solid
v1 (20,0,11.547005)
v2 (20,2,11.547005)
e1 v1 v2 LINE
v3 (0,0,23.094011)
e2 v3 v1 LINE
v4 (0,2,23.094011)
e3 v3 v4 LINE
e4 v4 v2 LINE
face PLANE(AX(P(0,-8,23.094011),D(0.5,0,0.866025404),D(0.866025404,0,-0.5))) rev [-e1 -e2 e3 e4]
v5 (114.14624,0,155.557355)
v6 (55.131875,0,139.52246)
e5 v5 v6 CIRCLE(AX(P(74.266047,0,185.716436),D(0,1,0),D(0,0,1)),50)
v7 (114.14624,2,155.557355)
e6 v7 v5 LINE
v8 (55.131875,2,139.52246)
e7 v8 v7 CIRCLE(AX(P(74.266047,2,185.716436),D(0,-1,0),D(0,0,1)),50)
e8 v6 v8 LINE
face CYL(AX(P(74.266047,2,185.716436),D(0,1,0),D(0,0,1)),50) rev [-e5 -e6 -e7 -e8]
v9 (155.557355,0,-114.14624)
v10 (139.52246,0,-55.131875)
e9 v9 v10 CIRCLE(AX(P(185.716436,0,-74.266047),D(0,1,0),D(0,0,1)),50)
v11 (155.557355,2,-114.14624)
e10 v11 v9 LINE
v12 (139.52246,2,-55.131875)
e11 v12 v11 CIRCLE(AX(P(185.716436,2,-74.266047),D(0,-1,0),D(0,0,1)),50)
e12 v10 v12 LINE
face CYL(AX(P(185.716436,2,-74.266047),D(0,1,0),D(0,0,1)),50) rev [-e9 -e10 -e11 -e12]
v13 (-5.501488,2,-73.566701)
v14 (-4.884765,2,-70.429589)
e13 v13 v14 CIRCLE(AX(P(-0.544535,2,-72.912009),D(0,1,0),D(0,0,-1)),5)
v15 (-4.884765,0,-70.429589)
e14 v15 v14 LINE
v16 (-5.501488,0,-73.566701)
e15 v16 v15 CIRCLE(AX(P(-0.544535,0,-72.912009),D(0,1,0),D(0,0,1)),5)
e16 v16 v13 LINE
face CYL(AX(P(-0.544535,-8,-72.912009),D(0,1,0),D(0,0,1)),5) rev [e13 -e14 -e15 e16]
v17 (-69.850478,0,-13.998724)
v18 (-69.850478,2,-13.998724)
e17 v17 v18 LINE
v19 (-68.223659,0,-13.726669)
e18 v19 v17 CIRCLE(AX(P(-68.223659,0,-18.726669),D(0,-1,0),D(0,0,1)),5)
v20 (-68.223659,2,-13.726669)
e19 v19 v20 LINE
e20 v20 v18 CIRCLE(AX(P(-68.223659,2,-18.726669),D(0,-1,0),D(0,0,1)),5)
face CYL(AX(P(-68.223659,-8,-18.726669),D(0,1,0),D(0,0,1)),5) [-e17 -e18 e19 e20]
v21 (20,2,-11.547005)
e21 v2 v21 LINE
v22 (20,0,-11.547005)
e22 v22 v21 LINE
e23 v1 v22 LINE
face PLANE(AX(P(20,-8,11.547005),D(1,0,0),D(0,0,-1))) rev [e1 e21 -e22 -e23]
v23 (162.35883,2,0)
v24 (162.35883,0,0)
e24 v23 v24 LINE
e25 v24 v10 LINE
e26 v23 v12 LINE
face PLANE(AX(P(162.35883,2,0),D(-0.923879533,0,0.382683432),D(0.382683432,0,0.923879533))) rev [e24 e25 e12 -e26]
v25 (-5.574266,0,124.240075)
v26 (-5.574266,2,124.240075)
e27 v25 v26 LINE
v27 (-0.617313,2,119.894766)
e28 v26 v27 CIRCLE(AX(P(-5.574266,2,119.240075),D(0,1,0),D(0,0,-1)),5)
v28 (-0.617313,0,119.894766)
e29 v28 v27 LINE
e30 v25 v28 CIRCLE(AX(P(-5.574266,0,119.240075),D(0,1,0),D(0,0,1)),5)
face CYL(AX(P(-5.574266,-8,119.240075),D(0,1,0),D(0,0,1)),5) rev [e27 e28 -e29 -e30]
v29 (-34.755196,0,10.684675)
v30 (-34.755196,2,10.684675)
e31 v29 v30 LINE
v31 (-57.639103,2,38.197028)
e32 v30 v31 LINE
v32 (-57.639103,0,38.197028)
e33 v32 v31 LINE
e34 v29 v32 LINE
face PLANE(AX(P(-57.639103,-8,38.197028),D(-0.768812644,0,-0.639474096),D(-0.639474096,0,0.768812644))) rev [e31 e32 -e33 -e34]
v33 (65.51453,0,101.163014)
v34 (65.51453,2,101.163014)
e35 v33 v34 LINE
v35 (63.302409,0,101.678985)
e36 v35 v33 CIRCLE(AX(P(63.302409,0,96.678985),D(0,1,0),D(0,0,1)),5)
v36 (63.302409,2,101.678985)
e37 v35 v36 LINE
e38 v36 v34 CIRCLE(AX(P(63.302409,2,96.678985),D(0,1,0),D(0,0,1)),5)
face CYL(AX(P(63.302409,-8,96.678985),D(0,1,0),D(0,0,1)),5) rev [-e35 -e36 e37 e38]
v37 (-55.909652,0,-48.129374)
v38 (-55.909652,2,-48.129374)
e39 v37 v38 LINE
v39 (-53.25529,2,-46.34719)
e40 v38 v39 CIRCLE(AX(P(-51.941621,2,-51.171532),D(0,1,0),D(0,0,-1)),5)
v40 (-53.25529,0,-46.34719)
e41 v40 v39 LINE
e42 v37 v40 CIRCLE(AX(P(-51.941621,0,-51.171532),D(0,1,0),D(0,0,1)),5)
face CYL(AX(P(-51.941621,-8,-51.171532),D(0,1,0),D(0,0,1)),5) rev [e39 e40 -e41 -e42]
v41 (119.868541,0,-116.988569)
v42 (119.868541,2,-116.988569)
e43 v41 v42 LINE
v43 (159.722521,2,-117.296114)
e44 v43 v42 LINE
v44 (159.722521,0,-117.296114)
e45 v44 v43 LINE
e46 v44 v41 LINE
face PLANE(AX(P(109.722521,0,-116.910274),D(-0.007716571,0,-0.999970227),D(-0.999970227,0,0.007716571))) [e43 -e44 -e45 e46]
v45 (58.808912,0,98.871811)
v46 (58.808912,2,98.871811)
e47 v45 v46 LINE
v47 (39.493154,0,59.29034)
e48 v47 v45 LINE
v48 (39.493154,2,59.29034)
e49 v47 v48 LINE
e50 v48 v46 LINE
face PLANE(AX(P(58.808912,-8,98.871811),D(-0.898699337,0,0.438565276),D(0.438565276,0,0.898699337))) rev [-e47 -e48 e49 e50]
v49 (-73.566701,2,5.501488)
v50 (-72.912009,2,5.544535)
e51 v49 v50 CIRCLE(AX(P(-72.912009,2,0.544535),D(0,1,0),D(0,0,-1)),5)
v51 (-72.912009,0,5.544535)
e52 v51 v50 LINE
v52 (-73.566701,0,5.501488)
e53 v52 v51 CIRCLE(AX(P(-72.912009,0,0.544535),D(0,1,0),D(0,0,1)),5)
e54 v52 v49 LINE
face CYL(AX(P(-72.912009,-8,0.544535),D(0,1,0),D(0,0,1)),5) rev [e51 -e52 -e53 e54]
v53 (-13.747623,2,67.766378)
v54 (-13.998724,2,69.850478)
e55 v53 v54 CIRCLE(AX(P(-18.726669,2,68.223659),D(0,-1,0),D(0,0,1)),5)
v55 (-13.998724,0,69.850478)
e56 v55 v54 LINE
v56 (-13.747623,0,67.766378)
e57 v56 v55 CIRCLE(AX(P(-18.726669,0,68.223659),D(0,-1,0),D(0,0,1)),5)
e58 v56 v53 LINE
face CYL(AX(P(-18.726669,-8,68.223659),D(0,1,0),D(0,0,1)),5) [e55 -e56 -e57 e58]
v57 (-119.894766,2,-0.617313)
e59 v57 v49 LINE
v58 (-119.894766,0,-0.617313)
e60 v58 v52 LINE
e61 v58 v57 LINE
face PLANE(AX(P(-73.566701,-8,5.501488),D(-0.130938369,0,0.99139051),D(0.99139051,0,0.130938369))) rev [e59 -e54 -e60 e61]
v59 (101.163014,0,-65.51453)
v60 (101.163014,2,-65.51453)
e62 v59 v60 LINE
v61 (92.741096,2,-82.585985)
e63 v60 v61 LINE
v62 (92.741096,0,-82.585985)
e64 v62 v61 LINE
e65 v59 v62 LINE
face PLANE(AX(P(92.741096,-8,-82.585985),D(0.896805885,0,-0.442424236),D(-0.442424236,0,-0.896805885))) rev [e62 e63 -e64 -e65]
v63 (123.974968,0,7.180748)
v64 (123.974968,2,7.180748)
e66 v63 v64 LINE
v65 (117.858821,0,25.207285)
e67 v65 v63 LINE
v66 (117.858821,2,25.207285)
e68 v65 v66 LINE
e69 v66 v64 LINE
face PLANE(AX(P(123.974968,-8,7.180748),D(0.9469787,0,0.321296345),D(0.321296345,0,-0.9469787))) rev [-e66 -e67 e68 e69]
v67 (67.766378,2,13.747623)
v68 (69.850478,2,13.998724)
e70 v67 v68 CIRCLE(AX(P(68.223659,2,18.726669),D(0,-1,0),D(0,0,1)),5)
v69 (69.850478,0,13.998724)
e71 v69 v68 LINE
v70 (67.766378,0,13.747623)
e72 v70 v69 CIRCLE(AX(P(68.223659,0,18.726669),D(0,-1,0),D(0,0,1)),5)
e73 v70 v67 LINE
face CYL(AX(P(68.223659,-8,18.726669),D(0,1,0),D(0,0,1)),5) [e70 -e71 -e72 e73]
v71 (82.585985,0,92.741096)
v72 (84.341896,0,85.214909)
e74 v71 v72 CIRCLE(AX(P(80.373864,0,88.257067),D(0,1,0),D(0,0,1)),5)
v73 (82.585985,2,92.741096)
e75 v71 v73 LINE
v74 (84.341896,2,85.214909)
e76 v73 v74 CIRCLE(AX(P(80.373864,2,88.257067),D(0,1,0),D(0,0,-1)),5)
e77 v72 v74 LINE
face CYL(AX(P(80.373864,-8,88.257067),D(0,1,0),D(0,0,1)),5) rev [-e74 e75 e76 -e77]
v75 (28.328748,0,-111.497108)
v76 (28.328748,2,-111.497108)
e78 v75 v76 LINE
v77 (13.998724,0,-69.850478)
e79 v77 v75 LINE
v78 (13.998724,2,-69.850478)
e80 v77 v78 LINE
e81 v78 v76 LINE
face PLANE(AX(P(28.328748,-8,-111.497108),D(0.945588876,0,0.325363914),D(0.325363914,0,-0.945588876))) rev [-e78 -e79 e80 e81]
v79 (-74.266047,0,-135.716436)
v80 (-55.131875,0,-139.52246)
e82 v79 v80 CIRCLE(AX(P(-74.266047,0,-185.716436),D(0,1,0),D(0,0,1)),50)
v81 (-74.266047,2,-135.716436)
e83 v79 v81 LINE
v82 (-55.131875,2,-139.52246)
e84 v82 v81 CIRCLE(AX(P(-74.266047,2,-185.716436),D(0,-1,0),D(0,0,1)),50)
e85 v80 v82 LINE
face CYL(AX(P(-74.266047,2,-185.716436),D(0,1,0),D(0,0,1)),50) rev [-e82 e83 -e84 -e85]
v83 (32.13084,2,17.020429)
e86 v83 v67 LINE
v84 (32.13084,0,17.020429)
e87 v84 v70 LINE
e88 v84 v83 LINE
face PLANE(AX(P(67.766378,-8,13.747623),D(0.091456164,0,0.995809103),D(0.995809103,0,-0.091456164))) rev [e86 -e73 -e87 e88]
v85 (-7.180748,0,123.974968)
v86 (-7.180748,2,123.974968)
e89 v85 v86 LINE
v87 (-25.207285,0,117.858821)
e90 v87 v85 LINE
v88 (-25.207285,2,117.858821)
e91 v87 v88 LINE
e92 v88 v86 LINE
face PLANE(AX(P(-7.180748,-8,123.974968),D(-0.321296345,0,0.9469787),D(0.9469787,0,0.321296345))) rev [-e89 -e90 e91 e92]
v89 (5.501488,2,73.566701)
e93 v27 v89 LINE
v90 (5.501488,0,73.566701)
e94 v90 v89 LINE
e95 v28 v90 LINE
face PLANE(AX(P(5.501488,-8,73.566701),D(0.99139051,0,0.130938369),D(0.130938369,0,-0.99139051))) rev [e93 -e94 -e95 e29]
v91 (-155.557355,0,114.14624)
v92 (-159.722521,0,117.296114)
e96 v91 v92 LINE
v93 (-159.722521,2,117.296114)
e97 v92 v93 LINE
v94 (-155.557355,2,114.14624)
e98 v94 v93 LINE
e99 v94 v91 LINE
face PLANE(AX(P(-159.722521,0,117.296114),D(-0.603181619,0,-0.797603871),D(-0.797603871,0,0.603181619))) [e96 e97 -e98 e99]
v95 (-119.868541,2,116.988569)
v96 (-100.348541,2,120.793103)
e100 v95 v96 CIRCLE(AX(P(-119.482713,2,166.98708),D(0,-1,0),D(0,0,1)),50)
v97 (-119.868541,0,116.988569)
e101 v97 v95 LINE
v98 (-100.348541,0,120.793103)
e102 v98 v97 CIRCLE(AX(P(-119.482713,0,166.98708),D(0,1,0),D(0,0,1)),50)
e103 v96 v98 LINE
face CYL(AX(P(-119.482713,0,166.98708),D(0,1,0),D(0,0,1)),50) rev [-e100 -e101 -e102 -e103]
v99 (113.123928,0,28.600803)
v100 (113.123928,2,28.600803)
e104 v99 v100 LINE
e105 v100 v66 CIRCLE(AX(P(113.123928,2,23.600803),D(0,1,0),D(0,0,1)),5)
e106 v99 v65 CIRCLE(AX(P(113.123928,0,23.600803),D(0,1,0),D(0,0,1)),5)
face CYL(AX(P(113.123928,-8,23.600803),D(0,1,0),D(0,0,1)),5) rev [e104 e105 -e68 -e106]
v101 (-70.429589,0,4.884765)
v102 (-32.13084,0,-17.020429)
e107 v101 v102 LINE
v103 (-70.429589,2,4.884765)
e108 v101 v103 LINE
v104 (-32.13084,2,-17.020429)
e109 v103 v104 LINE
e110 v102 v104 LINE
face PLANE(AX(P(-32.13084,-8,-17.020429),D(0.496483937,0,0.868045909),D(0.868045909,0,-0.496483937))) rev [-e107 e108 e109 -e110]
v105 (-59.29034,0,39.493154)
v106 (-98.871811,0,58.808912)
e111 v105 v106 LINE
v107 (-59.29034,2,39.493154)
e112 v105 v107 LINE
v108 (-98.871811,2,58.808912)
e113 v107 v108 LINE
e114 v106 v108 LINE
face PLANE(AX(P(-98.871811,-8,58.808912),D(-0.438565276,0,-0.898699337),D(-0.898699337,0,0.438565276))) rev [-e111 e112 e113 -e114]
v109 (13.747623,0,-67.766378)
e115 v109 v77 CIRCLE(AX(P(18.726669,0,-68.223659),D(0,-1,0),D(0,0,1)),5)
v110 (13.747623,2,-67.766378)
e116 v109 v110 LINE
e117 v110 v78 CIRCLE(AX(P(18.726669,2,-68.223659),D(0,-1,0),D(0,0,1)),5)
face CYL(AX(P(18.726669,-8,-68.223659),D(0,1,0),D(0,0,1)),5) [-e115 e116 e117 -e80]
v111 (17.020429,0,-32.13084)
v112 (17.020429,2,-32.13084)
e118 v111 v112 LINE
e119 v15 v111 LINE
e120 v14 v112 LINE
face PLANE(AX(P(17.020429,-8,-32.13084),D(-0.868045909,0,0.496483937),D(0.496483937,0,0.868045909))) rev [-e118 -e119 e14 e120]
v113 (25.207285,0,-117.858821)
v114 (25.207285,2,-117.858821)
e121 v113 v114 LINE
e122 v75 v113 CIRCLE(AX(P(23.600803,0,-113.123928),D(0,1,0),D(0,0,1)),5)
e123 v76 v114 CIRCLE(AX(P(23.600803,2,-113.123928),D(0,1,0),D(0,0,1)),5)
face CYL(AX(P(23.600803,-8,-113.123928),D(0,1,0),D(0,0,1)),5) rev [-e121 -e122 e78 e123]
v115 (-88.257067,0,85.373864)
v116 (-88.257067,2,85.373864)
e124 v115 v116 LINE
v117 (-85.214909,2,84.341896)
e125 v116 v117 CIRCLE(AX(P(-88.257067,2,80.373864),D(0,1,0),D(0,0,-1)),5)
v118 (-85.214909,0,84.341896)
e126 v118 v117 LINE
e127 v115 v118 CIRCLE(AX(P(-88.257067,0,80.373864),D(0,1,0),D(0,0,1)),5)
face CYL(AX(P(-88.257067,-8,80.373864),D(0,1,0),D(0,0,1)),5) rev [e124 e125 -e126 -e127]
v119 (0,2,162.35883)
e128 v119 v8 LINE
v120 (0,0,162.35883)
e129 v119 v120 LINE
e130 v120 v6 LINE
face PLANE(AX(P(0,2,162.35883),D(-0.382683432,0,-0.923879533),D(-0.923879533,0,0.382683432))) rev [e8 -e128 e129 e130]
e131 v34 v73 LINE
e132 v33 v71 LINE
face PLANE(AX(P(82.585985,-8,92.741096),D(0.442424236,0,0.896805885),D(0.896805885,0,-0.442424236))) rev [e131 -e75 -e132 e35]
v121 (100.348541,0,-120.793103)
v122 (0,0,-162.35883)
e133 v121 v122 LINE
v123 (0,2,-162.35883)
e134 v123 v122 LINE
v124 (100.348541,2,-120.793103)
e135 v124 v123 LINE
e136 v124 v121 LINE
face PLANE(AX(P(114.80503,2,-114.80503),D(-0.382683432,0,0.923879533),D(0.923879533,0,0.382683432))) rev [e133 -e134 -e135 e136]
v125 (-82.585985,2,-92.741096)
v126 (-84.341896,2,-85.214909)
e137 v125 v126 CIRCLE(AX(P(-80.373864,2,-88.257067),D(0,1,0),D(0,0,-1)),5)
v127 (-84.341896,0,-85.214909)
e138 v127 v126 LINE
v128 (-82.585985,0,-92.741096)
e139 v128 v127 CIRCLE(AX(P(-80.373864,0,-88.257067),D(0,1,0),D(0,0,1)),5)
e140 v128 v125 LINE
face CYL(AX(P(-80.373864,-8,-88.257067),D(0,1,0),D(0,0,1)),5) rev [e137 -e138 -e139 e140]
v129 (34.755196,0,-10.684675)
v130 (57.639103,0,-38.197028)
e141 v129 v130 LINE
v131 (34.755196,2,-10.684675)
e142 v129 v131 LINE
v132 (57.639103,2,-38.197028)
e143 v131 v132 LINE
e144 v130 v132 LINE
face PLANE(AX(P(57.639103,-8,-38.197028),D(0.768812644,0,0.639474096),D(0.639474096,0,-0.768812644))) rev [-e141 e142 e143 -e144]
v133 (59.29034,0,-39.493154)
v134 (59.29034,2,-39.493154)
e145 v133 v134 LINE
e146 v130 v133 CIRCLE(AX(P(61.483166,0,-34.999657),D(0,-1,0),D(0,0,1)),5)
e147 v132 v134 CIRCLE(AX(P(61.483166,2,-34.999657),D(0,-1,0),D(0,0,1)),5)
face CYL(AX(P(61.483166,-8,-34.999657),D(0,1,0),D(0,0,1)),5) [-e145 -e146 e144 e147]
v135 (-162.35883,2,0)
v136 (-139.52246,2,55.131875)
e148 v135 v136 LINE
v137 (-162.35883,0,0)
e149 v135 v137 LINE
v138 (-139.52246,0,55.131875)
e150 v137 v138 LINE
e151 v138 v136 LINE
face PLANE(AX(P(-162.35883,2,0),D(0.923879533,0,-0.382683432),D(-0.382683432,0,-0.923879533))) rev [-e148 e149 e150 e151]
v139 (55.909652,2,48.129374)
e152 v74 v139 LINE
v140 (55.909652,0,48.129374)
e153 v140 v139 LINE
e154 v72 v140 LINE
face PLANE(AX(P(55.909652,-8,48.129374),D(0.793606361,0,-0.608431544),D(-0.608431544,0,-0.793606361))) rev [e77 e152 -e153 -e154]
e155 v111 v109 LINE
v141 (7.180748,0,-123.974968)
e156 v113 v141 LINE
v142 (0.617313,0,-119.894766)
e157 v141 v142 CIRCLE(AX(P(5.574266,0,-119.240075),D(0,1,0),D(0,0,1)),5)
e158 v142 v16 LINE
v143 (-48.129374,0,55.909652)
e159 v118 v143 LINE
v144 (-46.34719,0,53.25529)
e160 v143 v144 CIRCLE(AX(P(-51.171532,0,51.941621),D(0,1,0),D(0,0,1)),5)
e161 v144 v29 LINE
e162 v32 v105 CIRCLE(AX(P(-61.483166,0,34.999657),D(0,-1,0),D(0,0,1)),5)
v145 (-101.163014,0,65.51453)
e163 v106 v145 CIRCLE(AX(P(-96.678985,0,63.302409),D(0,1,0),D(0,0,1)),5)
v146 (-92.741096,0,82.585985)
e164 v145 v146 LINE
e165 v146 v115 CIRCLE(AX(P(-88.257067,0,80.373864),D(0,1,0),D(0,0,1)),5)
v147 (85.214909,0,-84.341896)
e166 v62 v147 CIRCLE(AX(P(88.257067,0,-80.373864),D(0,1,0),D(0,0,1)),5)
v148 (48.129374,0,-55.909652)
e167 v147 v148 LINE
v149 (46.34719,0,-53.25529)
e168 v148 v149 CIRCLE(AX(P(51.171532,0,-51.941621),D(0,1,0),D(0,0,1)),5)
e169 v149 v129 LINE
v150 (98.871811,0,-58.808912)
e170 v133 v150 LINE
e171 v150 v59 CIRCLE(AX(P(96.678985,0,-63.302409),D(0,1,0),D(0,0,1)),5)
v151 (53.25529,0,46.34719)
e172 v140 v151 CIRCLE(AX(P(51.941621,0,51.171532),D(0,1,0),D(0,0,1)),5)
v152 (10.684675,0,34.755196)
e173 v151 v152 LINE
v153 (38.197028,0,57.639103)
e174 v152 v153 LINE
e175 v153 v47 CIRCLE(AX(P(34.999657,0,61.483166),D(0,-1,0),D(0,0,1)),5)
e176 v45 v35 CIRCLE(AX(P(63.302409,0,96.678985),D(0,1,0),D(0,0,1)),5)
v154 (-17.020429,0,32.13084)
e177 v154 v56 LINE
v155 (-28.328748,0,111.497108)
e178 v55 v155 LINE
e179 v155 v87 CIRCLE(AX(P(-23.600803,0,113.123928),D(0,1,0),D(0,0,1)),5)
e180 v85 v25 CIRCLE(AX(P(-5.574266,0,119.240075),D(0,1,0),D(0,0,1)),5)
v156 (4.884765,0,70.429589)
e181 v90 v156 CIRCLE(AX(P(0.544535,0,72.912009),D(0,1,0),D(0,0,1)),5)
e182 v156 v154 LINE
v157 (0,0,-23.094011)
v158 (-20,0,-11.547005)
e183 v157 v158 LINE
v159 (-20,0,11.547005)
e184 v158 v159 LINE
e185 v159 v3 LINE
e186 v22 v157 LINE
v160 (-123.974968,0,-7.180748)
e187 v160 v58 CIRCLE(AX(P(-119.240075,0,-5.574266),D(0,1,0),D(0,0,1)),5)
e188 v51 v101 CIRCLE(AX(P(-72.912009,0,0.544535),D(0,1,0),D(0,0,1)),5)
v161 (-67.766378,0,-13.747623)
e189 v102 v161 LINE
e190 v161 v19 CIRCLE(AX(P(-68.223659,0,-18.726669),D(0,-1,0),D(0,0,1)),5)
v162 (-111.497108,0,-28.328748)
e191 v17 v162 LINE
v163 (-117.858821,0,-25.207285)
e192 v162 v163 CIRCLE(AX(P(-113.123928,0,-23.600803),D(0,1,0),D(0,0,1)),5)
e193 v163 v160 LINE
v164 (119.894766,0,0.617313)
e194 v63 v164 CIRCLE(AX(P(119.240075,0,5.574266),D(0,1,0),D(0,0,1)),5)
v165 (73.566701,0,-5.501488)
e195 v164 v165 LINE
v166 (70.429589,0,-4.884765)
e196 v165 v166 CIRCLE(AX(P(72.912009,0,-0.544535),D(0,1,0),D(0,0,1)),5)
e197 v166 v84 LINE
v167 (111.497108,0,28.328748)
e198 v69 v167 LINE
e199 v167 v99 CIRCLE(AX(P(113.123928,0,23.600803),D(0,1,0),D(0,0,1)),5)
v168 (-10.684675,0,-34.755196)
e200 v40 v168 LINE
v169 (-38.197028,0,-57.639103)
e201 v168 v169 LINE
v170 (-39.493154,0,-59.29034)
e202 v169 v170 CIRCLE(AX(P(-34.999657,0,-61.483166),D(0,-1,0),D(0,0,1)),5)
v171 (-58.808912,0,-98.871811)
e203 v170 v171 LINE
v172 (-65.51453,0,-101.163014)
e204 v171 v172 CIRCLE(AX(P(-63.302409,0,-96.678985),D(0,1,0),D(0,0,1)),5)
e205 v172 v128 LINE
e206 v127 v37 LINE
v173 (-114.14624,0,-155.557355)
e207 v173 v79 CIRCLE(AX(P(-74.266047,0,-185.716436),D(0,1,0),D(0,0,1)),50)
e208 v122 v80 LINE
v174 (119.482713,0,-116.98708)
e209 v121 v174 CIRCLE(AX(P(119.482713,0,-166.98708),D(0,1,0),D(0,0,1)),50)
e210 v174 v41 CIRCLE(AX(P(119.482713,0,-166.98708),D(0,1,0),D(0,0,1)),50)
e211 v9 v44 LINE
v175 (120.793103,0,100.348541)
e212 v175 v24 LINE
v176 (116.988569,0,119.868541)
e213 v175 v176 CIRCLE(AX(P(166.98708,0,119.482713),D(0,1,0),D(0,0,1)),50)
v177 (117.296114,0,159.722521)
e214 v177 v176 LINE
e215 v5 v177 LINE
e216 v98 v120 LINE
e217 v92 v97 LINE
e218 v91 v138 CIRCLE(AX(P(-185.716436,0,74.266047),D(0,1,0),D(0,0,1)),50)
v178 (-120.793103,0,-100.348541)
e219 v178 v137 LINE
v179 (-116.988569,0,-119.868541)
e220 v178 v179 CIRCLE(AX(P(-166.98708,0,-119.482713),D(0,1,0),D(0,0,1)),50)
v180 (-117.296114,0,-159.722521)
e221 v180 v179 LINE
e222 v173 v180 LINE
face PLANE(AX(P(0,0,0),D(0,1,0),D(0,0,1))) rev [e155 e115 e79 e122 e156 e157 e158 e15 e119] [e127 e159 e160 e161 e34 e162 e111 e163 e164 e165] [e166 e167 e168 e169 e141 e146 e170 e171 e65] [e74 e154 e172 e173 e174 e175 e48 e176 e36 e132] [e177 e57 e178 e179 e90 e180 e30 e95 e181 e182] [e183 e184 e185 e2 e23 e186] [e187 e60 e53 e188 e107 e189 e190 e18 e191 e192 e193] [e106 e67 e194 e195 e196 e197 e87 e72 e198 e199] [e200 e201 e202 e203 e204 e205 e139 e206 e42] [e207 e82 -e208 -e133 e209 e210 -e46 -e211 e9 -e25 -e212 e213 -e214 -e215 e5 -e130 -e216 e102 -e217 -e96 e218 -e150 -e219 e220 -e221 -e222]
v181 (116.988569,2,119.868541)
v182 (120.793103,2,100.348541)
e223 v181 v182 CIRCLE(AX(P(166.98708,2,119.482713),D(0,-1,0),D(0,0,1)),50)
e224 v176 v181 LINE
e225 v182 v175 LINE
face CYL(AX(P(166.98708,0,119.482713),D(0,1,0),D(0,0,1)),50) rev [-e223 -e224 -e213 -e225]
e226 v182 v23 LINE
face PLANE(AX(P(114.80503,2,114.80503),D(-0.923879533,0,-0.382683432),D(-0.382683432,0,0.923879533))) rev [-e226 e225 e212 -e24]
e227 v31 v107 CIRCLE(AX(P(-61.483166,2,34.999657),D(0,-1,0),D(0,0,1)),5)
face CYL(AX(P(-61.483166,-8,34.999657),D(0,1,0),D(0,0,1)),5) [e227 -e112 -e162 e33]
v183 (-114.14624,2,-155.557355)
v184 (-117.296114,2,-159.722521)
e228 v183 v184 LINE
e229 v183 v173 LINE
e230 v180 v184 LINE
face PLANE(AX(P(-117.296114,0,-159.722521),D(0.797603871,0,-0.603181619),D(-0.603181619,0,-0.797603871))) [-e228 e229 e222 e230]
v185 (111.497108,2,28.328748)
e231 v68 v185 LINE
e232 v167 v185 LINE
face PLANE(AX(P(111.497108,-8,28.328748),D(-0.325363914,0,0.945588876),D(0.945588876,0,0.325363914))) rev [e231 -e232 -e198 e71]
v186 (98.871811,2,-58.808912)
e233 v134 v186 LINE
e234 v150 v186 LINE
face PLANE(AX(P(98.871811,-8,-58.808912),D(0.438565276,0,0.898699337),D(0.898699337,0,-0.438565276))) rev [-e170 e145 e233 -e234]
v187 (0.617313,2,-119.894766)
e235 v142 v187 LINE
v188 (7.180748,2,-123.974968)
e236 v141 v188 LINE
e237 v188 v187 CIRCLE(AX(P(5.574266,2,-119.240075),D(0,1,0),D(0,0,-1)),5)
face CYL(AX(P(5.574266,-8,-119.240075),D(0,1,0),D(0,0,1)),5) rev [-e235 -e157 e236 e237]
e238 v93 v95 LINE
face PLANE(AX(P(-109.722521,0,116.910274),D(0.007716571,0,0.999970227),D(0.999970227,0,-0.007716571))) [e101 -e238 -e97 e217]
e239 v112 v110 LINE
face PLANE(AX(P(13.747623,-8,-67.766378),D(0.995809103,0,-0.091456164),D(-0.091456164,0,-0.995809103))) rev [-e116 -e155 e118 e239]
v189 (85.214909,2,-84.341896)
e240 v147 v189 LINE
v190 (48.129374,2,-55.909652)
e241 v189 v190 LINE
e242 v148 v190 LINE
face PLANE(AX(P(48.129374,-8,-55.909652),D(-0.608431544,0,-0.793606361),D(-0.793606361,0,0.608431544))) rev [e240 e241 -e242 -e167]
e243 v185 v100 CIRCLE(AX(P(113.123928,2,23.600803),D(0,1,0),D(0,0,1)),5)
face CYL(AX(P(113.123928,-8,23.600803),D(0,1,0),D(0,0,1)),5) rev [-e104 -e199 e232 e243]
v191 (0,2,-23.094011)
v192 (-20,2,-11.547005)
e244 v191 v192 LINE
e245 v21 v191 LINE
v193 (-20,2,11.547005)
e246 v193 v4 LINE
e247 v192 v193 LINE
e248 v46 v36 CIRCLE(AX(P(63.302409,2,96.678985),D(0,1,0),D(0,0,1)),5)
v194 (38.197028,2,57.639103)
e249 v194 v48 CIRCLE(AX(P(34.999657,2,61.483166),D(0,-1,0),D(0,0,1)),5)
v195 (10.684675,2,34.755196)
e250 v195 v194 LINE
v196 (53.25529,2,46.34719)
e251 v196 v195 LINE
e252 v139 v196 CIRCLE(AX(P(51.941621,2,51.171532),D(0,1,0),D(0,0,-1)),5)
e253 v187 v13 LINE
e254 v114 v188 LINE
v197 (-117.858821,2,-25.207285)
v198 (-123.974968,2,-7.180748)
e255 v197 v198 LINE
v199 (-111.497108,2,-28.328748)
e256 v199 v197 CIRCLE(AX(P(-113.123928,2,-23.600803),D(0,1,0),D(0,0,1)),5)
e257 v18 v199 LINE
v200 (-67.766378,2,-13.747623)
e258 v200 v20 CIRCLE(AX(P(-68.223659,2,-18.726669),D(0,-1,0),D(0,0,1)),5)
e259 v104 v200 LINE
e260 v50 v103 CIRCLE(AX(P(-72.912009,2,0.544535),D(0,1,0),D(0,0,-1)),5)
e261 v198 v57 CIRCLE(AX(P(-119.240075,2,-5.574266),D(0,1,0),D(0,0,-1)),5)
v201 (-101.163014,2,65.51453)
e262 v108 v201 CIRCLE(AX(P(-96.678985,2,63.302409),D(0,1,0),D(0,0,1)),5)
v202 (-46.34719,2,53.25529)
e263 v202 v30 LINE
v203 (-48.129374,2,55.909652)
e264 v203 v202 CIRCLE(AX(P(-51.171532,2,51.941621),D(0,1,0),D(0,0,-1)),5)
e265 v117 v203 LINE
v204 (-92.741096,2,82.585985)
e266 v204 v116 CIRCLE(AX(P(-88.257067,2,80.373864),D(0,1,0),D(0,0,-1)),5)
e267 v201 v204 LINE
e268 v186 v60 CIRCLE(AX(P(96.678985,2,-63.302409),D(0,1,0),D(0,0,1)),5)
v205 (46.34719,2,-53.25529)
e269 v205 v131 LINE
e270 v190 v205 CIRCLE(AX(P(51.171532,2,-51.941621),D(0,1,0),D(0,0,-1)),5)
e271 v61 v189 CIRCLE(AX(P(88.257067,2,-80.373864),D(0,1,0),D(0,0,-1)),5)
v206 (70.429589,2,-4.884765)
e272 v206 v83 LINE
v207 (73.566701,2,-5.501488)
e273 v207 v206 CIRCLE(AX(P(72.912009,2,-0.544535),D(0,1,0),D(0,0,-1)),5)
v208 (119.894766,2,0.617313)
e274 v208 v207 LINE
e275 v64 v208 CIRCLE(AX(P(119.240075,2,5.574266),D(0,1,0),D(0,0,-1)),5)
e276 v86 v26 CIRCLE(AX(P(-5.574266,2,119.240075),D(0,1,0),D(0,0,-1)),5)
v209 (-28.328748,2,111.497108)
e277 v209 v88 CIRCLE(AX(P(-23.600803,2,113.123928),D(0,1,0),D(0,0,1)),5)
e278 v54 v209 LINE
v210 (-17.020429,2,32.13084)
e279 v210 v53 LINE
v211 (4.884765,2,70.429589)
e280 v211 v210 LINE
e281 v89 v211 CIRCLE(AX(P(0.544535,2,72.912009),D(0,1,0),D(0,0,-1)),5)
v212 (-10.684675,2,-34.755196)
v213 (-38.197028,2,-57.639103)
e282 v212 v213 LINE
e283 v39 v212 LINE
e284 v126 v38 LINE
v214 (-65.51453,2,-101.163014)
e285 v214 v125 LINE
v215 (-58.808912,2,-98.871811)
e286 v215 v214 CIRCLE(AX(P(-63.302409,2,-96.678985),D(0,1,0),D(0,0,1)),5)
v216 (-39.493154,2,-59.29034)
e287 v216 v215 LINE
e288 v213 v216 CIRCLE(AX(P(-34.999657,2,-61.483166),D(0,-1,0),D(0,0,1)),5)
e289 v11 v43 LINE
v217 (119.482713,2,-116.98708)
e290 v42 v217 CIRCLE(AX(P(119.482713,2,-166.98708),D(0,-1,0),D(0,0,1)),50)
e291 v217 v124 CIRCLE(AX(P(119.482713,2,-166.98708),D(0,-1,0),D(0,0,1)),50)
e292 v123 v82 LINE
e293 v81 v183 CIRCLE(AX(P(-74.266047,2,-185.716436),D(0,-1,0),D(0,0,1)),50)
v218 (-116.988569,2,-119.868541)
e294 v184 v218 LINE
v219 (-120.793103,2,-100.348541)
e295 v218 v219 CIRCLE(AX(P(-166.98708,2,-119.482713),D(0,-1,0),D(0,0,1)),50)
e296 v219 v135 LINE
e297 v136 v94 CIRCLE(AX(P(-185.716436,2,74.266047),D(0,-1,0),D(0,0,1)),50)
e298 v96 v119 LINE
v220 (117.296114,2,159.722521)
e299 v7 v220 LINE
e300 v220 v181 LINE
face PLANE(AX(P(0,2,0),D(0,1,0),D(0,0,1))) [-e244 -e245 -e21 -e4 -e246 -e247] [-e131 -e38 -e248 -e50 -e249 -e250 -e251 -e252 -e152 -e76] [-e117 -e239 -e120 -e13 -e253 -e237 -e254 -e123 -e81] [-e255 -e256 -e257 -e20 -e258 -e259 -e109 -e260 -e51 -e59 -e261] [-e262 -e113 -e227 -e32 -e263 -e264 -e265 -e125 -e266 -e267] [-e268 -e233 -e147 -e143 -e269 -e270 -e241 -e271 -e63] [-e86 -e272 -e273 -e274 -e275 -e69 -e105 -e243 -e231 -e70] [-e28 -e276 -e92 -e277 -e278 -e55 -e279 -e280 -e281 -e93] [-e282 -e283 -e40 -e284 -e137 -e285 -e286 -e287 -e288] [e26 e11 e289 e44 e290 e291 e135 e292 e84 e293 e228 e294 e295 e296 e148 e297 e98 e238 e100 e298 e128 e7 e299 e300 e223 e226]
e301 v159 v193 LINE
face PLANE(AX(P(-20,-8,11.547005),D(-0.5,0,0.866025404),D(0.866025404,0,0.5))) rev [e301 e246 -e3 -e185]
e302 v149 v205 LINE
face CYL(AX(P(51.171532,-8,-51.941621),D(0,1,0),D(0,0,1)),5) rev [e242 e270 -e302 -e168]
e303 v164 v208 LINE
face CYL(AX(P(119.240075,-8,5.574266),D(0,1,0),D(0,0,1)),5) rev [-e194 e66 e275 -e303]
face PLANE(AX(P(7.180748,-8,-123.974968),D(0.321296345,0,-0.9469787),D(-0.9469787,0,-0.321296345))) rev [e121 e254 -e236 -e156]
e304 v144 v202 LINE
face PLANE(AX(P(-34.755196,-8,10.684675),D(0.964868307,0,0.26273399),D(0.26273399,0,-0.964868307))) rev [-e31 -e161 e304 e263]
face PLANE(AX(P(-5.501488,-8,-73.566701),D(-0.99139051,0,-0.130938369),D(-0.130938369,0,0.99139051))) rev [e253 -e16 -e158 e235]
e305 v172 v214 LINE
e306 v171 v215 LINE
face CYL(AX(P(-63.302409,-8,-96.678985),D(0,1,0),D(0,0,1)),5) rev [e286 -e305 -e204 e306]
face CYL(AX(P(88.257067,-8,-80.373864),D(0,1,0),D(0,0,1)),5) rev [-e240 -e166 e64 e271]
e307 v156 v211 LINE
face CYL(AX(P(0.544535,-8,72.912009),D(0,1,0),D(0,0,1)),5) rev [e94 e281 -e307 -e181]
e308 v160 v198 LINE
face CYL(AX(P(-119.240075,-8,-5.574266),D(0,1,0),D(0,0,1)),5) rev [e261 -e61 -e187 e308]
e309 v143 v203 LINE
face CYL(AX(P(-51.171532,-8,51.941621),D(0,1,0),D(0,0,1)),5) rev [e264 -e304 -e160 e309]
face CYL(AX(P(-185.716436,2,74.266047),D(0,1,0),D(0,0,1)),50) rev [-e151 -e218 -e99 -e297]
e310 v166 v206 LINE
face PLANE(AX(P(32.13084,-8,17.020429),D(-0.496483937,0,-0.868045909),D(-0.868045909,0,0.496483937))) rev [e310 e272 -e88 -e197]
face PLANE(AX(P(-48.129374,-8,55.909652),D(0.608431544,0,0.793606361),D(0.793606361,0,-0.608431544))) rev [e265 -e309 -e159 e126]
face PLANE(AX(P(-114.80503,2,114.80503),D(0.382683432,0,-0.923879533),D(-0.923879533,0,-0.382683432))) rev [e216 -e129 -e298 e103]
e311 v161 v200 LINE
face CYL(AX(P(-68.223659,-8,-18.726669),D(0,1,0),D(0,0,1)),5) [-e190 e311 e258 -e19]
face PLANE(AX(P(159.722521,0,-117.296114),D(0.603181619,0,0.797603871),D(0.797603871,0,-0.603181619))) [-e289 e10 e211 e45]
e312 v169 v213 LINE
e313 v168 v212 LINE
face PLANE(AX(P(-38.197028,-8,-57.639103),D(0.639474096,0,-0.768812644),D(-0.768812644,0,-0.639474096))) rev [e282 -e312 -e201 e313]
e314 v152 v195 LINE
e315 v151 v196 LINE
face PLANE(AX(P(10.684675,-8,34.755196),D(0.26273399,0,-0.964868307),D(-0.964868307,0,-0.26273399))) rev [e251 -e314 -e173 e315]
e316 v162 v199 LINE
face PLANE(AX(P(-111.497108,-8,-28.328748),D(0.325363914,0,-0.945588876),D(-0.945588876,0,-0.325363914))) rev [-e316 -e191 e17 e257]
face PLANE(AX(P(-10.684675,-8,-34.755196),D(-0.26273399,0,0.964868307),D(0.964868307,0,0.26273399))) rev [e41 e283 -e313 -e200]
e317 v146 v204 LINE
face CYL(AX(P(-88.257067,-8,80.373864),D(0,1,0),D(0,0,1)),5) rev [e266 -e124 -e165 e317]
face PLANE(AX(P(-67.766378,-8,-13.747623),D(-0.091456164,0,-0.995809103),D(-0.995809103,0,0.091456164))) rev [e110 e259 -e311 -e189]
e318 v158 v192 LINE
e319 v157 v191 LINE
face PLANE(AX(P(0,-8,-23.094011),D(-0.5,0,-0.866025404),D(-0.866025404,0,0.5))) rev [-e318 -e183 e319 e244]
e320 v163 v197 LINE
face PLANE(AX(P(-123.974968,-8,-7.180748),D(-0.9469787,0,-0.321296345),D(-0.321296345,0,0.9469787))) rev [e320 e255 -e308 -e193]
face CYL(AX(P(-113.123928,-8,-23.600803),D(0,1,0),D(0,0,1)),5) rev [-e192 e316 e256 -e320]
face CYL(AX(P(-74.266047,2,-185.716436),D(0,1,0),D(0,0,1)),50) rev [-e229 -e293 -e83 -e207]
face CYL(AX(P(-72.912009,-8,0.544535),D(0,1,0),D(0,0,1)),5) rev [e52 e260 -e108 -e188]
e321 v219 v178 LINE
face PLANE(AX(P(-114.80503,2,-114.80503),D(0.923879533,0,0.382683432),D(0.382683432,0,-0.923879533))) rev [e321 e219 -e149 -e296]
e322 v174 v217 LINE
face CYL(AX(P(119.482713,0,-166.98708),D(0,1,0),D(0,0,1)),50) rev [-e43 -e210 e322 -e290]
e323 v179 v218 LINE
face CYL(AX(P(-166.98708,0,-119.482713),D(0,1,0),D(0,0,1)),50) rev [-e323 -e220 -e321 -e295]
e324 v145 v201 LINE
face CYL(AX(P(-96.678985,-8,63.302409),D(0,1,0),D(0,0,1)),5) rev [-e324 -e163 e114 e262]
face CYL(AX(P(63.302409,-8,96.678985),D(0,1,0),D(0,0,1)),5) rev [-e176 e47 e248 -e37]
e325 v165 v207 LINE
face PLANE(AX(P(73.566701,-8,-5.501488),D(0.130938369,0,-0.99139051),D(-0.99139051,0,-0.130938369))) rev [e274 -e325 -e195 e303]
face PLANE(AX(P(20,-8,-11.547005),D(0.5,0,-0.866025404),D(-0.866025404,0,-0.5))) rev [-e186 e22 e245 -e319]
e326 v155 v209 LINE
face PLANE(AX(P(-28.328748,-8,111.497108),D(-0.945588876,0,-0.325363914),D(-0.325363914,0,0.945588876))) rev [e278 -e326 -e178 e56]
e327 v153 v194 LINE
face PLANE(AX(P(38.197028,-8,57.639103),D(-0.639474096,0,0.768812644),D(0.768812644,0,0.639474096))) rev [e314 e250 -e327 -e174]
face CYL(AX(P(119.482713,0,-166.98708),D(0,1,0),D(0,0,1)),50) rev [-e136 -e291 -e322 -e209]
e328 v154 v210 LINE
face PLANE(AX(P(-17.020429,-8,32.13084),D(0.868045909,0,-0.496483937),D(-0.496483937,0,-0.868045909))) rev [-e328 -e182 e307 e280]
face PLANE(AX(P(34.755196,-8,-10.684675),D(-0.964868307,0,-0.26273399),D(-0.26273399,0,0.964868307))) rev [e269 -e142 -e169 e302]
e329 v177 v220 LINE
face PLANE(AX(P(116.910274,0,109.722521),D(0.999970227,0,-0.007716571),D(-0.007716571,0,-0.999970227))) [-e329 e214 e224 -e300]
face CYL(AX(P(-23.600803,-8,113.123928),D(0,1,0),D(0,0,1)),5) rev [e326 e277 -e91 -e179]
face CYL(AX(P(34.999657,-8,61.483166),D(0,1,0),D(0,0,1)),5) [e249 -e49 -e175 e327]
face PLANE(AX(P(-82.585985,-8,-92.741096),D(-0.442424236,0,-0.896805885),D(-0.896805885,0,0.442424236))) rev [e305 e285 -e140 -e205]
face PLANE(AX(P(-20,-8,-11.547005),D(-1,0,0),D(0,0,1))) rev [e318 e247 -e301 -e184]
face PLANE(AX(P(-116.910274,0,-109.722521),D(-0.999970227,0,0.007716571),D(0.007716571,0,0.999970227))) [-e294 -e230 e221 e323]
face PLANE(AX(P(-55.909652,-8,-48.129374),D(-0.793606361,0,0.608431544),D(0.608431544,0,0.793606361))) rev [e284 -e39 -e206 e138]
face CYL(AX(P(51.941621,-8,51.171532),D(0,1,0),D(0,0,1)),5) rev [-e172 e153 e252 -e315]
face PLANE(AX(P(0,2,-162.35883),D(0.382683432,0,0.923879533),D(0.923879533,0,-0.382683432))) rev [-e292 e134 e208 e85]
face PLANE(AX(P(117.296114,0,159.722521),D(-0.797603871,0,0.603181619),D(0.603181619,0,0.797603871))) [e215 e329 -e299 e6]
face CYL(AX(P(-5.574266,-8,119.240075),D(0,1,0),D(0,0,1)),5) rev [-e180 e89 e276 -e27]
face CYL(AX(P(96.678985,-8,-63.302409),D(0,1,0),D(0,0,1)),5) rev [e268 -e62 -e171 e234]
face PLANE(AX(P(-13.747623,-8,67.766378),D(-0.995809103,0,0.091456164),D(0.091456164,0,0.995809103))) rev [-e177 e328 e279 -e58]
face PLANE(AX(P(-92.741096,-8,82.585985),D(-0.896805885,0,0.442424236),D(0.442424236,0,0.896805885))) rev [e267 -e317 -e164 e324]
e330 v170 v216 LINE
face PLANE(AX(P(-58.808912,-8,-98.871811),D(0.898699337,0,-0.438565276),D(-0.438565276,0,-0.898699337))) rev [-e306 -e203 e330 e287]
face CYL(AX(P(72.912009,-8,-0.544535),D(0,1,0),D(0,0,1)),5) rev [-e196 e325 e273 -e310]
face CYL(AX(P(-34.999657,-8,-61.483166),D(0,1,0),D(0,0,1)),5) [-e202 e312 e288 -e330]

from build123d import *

# Parameters (mm, degrees)
BOSS_EXTRUDE1_DEPTH = 2
CUT_EXTRUDE1_DEPTH  = 10
CUT_EXTRUDE2_DEPTH  = 10
BOSS_EXTRUDE2_DEPTH = 2
FILLET1_R           = 50


with BuildPart() as part:
    # Sketch1 → Boss-Extrude1 (new body)
    with BuildSketch(Plane(origin=(0, 0, 0), x_dir=(1, 0, 0), z_dir=(0, 1, 0))):
        Polygon((114.80502971, -114.80502971), (162.358830044, 0), (114.80502971, 114.80502971), (0, 162.358830044), (-114.80502971, 114.80502971), (-162.358830044, 0), (-114.80502971, -114.80502971), (0, -162.358830044), align=None)
    extrude(amount=BOSS_EXTRUDE1_DEPTH)

    # Sketch2 → Cut-Extrude1 (cut)
    with BuildSketch(Plane(origin=(0, 2, 0), x_dir=(1, 0, 0), z_dir=(0, 1, 0))):
        Polygon((20, 11.547005384), (0, 23.094010768), (-20, 11.547005384), (-20, -11.547005384), (0, -23.094010768), (20, -11.547005384), align=None)
    extrude(amount=-CUT_EXTRUDE1_DEPTH, mode=Mode.SUBTRACT)

    # Sketch3 → Cut-Extrude2 (cut)
    with BuildSketch(Plane(origin=(0, 2, 0), x_dir=(1, 0, 0), z_dir=(0, 1, 0))):
        with BuildLine():
            Line((7.180747689, 123.974968015), (25.207285, 117.858821427))
            ThreePointArc((25.207285, 117.858821427), (28.089576698, 115.326406795), (28.328747659, 111.497108353))
            Line((28.328747659, 111.497108353), (13.99872444, 69.850478373))
            ThreePointArc((13.99872444, 69.850478373), (13.762569524, 68.82175425), (13.747623306, 67.766377979))
            Line((13.747623306, 67.766377979), (17.02042887, 32.130840461))
            Line((17.02042887, 32.130840461), (-4.884764675, 70.429589412))
            ThreePointArc((-4.884764675, 70.429589412), (-5.450629901, 71.947522663), (-5.501487679, 73.566700941))
            Line((-5.501487679, 73.566700941), (0.617313414, 119.89476636))
            ThreePointArc((0.617313414, 119.89476636), (2.934488498, 123.486434711), (7.180747689, 123.974968015))
        make_face()
        with BuildLine():
            Line((92.741095966, 82.585985196), (101.163014013, 65.514529695))
            ThreePointArc((101.163014013, 65.514529695), (101.410414459, 61.68575413), (98.871810971, 58.808911827))
            Line((98.871810971, 58.808911827), (59.290339906, 39.493153947))
            ThreePointArc((59.290339906, 39.493153947), (58.395935361, 38.932722886), (57.63910307, 38.197027741))
            Line((57.63910307, 38.197027741), (34.755195848, 10.684674503))
            Line((34.755195848, 10.684674503), (46.347190043, 53.255290495))
            ThreePointArc((46.347190043, 53.255290495), (47.0204038, 54.72875853), (48.129373861, 55.909652349))
            Line((48.129373861, 55.909652349), (85.214908823, 84.34189582))
            ThreePointArc((85.214908823, 84.34189582), (89.393092084, 85.243098653), (92.741095966, 82.585985196))
        make_face()
        with BuildLine():
            Line((123.974968015, -7.180747689), (117.858821427, -25.207285))
            ThreePointArc((117.858821427, -25.207285), (115.326406795, -28.089576698), (111.497108353, -28.328747659))
            Line((111.497108353, -28.328747659), (69.850478373, -13.99872444))
            ThreePointArc((69.850478373, -13.99872444), (68.82175425, -13.762569524), (67.766377979, -13.747623306))
            Line((67.766377979, -13.747623306), (32.130840461, -17.02042887))
            Line((32.130840461, -17.02042887), (70.429589412, 4.884764675))
            ThreePointArc((70.429589412, 4.884764675), (71.947522663, 5.450629901), (73.566700941, 5.501487679))
            Line((73.566700941, 5.501487679), (119.89476636, -0.617313414))
            ThreePointArc((119.89476636, -0.617313414), (123.486434711, -2.934488498), (123.974968015, -7.180747689))
        make_face()
        with BuildLine():
            Line((82.585985196, -92.741095966), (65.514529695, -101.163014013))
            ThreePointArc((65.514529695, -101.163014013), (61.68575413, -101.410414459), (58.808911827, -98.871810971))
            Line((58.808911827, -98.871810971), (39.493153947, -59.290339906))
            ThreePointArc((39.493153947, -59.290339906), (38.932722886, -58.395935361), (38.197027741, -57.63910307))
            Line((38.197027741, -57.63910307), (10.684674503, -34.755195848))
            Line((10.684674503, -34.755195848), (53.255290495, -46.347190043))
            ThreePointArc((53.255290495, -46.347190043), (54.72875853, -47.0204038), (55.909652349, -48.129373861))
            Line((55.909652349, -48.129373861), (84.34189582, -85.214908823))
            ThreePointArc((84.34189582, -85.214908823), (85.243098653, -89.393092084), (82.585985196, -92.741095966))
        make_face()
        with BuildLine():
            Line((-7.180747689, -123.974968015), (-25.207285, -117.858821427))
            ThreePointArc((-25.207285, -117.858821427), (-28.089576698, -115.326406795), (-28.328747659, -111.497108353))
            Line((-28.328747659, -111.497108353), (-13.99872444, -69.850478373))
            ThreePointArc((-13.99872444, -69.850478373), (-13.762569524, -68.82175425), (-13.747623306, -67.766377979))
            Line((-13.747623306, -67.766377979), (-17.02042887, -32.130840461))
            Line((-17.02042887, -32.130840461), (4.884764675, -70.429589412))
            ThreePointArc((4.884764675, -70.429589412), (5.450629901, -71.947522663), (5.501487679, -73.566700941))
            Line((5.501487679, -73.566700941), (-0.617313414, -119.89476636))
            ThreePointArc((-0.617313414, -119.89476636), (-2.934488497, -123.486434711), (-7.180747689, -123.974968015))
        make_face()
        with BuildLine():
            Line((-92.741095966, -82.585985196), (-101.163014013, -65.514529695))
            ThreePointArc((-101.163014013, -65.514529695), (-101.410414459, -61.68575413), (-98.871810971, -58.808911827))
            Line((-98.871810971, -58.808911827), (-59.290339906, -39.493153947))
            ThreePointArc((-59.290339906, -39.493153947), (-58.395935361, -38.932722886), (-57.63910307, -38.197027741))
            Line((-57.63910307, -38.197027741), (-34.755195848, -10.684674503))
            Line((-34.755195848, -10.684674503), (-46.347190043, -53.255290495))
            ThreePointArc((-46.347190043, -53.255290495), (-47.0204038, -54.72875853), (-48.129373861, -55.909652349))
            Line((-48.129373861, -55.909652349), (-85.214908823, -84.34189582))
            ThreePointArc((-85.214908823, -84.34189582), (-89.393092084, -85.243098653), (-92.741095966, -82.585985196))
        make_face()
        with BuildLine():
            Line((-123.974968015, 7.180747689), (-117.858821427, 25.207285))
            ThreePointArc((-117.858821427, 25.207285), (-115.326406795, 28.089576698), (-111.497108353, 28.328747659))
            Line((-111.497108353, 28.328747659), (-69.850478373, 13.99872444))
            ThreePointArc((-69.850478373, 13.99872444), (-68.82175425, 13.762569524), (-67.766377979, 13.747623306))
            Line((-67.766377979, 13.747623306), (-32.130840461, 17.02042887))
            Line((-32.130840461, 17.02042887), (-70.429589412, -4.884764675))
            ThreePointArc((-70.429589412, -4.884764675), (-71.947522663, -5.450629901), (-73.566700941, -5.501487679))
            Line((-73.566700941, -5.501487679), (-119.89476636, 0.617313414))
            ThreePointArc((-119.89476636, 0.617313414), (-123.486434711, 2.934488497), (-123.974968015, 7.180747689))
        make_face()
        with BuildLine():
            Line((-82.585985196, 92.741095966), (-65.514529695, 101.163014013))
            ThreePointArc((-65.514529695, 101.163014013), (-61.68575413, 101.410414459), (-58.808911827, 98.871810971))
            Line((-58.808911827, 98.871810971), (-39.493153947, 59.290339906))
            ThreePointArc((-39.493153947, 59.290339906), (-38.932722886, 58.395935361), (-38.197027741, 57.63910307))
            Line((-38.197027741, 57.63910307), (-10.684674503, 34.755195848))
            Line((-10.684674503, 34.755195848), (-53.255290495, 46.347190043))
            ThreePointArc((-53.255290495, 46.347190043), (-54.72875853, 47.0204038), (-55.909652349, 48.129373861))
            Line((-55.909652349, 48.129373861), (-84.34189582, 85.214908823))
            ThreePointArc((-84.34189582, 85.214908823), (-85.243098653, 89.393092084), (-82.585985196, 92.741095966))
        make_face()
    extrude(amount=-CUT_EXTRUDE2_DEPTH, mode=Mode.SUBTRACT)

    # Sketch6 → Boss-Extrude2 (add)
    with BuildSketch(Plane(origin=(0, 2, 0), x_dir=(1, 0, 0), z_dir=(0, 1, 0))):
        Polygon((-116.910273848, 109.722520758), (-117.296113887, 159.722520758), (-90.835857438, 124.733385943), (-114.80502971, 114.80502971), align=None)
        Polygon((109.722520758, 116.910273848), (159.722520758, 117.296113887), (124.733385943, 90.835857438), (114.80502971, 114.80502971), align=None)
        Polygon((116.910273848, -109.722520758), (117.296113887, -159.722520758), (90.835857438, -124.733385943), (114.80502971, -114.80502971), align=None)
        Polygon((-109.722520758, -116.910273848), (-159.722520758, -117.296113887), (-124.733385943, -90.835857438), (-114.80502971, -114.80502971), align=None)
    extrude(amount=-BOSS_EXTRUDE2_DEPTH)

    # Fillet1
    fillet1_edges = [part.edges().sort_by_distance(p)[0] for p in [
        (-116.910273848, 1, -109.722520758),
        (-90.835857438, 1, -124.733385943),
        (109.722520758, 1, -116.910273848),
        (124.733385943, 1, -90.835857438),
        (116.910273848, 1, 109.722520758),
        (90.835857438, 1, 124.733385943),
        (-109.722520758, 1, 116.910273848),
        (-124.733385943, 1, 90.835857438),
    ]]
    fillet(fillet1_edges, radius=FILLET1_R)


solid = part.part
